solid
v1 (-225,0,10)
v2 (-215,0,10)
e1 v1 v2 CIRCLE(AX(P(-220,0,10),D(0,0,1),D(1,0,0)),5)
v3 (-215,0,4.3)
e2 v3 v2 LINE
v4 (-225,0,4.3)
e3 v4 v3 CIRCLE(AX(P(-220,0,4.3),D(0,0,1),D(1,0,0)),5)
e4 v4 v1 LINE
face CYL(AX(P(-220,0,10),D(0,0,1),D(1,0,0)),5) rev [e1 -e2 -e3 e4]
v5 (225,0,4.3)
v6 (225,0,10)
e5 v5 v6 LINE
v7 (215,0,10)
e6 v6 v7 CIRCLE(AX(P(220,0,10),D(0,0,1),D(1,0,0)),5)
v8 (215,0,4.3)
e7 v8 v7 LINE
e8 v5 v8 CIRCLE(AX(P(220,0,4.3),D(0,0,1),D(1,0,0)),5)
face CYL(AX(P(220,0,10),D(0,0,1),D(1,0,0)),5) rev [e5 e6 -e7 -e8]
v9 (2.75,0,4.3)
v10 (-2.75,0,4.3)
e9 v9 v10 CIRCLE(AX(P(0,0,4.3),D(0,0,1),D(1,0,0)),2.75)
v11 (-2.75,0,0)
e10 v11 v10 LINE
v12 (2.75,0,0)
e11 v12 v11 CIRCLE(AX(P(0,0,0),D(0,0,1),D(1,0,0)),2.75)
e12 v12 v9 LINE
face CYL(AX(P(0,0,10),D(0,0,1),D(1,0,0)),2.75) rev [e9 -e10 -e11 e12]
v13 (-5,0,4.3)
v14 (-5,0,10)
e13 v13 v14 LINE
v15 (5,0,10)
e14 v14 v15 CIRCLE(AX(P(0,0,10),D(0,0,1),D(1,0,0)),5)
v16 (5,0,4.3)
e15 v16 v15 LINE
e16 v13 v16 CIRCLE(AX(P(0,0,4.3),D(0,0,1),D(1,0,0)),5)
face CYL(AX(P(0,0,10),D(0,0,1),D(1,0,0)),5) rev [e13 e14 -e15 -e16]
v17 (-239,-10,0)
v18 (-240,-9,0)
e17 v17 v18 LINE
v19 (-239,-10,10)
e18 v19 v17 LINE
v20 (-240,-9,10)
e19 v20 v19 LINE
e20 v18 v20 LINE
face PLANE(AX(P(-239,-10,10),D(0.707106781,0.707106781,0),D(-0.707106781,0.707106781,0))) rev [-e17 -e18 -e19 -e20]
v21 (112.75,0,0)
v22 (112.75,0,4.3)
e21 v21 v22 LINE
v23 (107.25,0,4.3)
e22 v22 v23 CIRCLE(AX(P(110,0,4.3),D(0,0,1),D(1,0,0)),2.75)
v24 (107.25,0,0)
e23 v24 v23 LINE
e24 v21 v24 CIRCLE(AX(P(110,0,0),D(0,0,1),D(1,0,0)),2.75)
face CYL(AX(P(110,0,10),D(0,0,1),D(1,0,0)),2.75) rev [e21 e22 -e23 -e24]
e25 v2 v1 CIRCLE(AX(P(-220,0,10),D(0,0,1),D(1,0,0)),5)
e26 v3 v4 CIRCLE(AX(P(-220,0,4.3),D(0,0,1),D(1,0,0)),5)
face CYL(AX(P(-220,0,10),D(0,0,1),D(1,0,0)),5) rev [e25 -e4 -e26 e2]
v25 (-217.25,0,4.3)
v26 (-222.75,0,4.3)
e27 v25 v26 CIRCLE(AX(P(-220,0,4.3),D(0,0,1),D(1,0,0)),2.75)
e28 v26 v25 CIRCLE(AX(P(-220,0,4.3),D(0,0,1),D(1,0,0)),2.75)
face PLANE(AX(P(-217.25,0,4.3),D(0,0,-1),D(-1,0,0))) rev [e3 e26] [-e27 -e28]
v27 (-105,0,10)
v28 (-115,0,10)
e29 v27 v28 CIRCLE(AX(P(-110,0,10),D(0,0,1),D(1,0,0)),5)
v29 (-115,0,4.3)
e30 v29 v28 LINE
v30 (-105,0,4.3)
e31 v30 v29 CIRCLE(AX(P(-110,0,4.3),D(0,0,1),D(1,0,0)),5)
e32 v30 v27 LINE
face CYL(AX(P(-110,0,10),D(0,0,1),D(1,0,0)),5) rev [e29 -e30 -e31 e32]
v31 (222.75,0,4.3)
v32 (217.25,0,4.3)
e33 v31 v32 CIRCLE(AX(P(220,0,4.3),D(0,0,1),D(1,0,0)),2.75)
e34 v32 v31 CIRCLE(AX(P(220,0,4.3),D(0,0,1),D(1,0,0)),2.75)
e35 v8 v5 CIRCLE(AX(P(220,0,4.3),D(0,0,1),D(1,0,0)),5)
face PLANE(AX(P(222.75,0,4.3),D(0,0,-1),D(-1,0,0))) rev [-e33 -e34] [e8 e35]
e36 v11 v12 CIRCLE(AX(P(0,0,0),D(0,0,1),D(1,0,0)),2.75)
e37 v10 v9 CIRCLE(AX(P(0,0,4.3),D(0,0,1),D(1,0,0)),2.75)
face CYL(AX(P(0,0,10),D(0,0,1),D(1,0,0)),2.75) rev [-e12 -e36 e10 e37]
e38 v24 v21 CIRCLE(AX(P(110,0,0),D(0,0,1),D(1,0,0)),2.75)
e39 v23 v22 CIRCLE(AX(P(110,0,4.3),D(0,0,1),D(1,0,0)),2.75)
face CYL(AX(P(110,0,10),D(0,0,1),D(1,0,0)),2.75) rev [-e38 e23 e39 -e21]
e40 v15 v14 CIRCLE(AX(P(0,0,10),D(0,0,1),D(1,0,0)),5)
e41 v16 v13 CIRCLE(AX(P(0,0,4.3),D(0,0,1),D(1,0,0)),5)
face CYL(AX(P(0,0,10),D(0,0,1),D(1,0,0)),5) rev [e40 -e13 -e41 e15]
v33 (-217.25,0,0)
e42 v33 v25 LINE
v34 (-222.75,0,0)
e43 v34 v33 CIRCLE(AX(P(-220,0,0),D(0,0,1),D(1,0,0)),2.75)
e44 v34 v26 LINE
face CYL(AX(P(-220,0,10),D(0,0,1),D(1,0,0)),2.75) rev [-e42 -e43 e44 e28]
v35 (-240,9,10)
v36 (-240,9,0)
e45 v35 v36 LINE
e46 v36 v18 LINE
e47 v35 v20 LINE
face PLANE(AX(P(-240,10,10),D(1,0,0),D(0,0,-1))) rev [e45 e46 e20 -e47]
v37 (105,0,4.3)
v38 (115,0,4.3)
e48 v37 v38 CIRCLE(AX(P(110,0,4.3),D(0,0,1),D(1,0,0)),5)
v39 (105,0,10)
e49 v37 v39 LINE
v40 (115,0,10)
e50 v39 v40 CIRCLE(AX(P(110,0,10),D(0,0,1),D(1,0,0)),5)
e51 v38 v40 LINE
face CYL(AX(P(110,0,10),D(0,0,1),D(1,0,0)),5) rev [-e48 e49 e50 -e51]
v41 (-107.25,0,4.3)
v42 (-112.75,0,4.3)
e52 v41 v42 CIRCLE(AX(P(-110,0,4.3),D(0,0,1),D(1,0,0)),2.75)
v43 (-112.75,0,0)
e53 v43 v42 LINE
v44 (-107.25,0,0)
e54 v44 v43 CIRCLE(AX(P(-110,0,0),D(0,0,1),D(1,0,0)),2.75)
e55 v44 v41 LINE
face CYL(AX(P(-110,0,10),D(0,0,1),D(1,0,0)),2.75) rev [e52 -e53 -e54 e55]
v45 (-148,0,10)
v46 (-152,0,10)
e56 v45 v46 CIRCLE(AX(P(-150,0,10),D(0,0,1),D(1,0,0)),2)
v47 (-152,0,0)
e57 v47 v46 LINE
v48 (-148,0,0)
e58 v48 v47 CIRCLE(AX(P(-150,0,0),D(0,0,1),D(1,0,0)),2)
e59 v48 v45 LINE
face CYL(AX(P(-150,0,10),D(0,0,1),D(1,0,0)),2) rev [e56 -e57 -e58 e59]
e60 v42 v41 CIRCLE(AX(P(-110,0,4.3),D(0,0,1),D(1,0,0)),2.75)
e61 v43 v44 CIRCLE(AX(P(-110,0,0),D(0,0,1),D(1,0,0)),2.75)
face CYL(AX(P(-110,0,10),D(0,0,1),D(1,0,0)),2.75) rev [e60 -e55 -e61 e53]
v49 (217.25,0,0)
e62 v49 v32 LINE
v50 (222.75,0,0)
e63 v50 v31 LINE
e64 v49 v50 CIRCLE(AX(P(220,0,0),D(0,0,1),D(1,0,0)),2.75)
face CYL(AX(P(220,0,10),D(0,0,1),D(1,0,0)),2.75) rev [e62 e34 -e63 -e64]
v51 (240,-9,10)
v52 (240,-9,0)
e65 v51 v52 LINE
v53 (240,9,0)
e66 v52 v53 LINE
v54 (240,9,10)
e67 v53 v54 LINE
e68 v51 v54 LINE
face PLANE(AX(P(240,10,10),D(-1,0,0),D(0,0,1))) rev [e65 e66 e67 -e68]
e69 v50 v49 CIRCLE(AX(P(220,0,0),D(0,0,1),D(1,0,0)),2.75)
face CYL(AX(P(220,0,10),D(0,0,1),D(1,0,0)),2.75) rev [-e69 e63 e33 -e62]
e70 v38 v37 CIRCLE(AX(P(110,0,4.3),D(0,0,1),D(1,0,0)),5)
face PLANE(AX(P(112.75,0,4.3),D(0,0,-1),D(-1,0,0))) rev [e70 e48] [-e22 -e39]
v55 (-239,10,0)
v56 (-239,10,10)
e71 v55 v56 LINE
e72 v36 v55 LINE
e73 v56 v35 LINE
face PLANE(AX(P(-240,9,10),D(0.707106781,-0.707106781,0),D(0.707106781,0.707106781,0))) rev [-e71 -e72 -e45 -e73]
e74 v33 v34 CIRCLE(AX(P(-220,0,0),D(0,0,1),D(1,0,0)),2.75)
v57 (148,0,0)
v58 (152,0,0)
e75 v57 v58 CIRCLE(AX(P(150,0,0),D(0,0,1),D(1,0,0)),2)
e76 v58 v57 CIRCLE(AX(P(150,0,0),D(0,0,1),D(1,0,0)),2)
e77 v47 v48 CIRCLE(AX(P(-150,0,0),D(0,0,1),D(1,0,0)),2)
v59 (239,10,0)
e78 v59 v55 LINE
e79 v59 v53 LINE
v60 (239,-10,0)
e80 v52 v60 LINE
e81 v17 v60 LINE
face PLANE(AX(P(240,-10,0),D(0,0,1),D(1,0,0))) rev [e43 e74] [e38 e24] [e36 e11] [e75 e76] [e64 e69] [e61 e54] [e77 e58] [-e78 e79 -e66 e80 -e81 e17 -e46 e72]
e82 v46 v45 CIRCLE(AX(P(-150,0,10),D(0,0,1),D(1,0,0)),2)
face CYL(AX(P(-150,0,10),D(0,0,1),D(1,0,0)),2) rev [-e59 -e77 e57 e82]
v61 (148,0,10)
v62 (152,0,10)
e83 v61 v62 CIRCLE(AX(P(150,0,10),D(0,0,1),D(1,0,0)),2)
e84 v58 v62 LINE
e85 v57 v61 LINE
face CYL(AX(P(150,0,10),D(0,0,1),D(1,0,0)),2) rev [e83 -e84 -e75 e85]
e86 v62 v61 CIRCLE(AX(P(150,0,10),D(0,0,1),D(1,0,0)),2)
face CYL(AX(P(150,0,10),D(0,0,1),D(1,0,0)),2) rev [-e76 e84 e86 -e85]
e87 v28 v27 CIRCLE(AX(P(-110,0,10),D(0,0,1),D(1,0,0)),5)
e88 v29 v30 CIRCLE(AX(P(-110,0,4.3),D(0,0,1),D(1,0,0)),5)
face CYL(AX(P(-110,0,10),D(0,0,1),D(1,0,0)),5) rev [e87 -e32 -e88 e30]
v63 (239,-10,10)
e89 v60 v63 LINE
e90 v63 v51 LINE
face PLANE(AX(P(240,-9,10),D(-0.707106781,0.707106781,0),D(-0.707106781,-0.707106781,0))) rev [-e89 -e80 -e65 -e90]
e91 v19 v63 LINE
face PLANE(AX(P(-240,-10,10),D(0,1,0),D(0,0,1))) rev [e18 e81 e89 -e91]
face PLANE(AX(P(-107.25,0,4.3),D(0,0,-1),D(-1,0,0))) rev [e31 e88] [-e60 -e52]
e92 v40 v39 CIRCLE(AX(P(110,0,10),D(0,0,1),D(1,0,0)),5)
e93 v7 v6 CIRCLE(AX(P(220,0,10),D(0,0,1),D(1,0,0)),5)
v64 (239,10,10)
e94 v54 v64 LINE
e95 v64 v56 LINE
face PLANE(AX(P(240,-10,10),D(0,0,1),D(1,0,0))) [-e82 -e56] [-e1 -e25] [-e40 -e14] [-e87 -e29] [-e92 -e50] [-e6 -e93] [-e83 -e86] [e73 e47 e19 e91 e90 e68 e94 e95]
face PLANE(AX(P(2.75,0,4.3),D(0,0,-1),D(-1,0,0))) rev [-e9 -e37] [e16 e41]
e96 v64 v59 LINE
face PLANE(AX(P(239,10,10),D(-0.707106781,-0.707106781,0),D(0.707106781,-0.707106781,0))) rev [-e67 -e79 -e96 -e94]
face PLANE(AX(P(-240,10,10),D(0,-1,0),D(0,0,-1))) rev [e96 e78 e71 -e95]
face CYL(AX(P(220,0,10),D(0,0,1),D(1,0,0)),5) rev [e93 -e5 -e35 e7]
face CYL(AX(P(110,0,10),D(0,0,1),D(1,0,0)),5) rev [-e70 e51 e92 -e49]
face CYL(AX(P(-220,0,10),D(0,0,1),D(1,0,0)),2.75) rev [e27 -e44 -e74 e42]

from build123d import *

# Parameters (mm, degrees)
SKETCH1_W                                            = 480
SKETCH1_H                                            = 20
BOSS_EXTRUDE1_DEPTH                                  = 10
HOLE_SIZE_PER_SOCKET_HEAD_CAP_SCREW_TYPE_D           = 5.5
HOLE_SIZE_PER_SOCKET_HEAD_CAP_SCREW_TYPE_CBORE_D     = 10
HOLE_SIZE_PER_SOCKET_HEAD_CAP_SCREW_TYPE_CBORE_DEPTH = 5.7
CHAMFER1_SIZE                                        = 1
F_4_0_4_DIAMETER_HOLE1_D                             = 4
F_4_0_4_DIAMETER_HOLE1_DEPTH                         = 12
F_4_0_4_DIAMETER_HOLE1_TIP                           = 1.201721238


with BuildPart() as part:
    # Sketch1 → Boss-Extrude1 (new body)
    with BuildSketch(Plane.XY):
        Rectangle(SKETCH1_W, SKETCH1_H)
    extrude(amount=BOSS_EXTRUDE1_DEPTH)

    # Hole size per socket head cap screw type1 (through all)
    with Locations(Plane.XY.offset(10)):
        with Locations((0, 0), (-110, 0), (110, 0), (220, 0), (-220, 0)):
            CounterBoreHole(HOLE_SIZE_PER_SOCKET_HEAD_CAP_SCREW_TYPE_D / 2, HOLE_SIZE_PER_SOCKET_HEAD_CAP_SCREW_TYPE_CBORE_D / 2, HOLE_SIZE_PER_SOCKET_HEAD_CAP_SCREW_TYPE_CBORE_DEPTH)

    # Chamfer1
    chamfer1_edges = [part.edges().sort_by_distance(p)[0] for p in [
        (240, -10, 5),
        (-240, -10, 5),
        (-240, 10, 5),
        (240, 10, 5),
    ]]
    chamfer(chamfer1_edges, length=CHAMFER1_SIZE)

    # Ø4.0 (4) Diameter Hole1
    with Locations(Plane.XY.offset(10)):
        with Locations((-150, 0), (150, 0)):
            Hole(F_4_0_4_DIAMETER_HOLE1_D / 2, depth=F_4_0_4_DIAMETER_HOLE1_DEPTH)
            with Locations((0, 0, -(F_4_0_4_DIAMETER_HOLE1_DEPTH + F_4_0_4_DIAMETER_HOLE1_TIP / 2))):  # 118° drill point
                Cone(0, F_4_0_4_DIAMETER_HOLE1_D / 2, F_4_0_4_DIAMETER_HOLE1_TIP, mode=Mode.SUBTRACT)


solid = part.part
